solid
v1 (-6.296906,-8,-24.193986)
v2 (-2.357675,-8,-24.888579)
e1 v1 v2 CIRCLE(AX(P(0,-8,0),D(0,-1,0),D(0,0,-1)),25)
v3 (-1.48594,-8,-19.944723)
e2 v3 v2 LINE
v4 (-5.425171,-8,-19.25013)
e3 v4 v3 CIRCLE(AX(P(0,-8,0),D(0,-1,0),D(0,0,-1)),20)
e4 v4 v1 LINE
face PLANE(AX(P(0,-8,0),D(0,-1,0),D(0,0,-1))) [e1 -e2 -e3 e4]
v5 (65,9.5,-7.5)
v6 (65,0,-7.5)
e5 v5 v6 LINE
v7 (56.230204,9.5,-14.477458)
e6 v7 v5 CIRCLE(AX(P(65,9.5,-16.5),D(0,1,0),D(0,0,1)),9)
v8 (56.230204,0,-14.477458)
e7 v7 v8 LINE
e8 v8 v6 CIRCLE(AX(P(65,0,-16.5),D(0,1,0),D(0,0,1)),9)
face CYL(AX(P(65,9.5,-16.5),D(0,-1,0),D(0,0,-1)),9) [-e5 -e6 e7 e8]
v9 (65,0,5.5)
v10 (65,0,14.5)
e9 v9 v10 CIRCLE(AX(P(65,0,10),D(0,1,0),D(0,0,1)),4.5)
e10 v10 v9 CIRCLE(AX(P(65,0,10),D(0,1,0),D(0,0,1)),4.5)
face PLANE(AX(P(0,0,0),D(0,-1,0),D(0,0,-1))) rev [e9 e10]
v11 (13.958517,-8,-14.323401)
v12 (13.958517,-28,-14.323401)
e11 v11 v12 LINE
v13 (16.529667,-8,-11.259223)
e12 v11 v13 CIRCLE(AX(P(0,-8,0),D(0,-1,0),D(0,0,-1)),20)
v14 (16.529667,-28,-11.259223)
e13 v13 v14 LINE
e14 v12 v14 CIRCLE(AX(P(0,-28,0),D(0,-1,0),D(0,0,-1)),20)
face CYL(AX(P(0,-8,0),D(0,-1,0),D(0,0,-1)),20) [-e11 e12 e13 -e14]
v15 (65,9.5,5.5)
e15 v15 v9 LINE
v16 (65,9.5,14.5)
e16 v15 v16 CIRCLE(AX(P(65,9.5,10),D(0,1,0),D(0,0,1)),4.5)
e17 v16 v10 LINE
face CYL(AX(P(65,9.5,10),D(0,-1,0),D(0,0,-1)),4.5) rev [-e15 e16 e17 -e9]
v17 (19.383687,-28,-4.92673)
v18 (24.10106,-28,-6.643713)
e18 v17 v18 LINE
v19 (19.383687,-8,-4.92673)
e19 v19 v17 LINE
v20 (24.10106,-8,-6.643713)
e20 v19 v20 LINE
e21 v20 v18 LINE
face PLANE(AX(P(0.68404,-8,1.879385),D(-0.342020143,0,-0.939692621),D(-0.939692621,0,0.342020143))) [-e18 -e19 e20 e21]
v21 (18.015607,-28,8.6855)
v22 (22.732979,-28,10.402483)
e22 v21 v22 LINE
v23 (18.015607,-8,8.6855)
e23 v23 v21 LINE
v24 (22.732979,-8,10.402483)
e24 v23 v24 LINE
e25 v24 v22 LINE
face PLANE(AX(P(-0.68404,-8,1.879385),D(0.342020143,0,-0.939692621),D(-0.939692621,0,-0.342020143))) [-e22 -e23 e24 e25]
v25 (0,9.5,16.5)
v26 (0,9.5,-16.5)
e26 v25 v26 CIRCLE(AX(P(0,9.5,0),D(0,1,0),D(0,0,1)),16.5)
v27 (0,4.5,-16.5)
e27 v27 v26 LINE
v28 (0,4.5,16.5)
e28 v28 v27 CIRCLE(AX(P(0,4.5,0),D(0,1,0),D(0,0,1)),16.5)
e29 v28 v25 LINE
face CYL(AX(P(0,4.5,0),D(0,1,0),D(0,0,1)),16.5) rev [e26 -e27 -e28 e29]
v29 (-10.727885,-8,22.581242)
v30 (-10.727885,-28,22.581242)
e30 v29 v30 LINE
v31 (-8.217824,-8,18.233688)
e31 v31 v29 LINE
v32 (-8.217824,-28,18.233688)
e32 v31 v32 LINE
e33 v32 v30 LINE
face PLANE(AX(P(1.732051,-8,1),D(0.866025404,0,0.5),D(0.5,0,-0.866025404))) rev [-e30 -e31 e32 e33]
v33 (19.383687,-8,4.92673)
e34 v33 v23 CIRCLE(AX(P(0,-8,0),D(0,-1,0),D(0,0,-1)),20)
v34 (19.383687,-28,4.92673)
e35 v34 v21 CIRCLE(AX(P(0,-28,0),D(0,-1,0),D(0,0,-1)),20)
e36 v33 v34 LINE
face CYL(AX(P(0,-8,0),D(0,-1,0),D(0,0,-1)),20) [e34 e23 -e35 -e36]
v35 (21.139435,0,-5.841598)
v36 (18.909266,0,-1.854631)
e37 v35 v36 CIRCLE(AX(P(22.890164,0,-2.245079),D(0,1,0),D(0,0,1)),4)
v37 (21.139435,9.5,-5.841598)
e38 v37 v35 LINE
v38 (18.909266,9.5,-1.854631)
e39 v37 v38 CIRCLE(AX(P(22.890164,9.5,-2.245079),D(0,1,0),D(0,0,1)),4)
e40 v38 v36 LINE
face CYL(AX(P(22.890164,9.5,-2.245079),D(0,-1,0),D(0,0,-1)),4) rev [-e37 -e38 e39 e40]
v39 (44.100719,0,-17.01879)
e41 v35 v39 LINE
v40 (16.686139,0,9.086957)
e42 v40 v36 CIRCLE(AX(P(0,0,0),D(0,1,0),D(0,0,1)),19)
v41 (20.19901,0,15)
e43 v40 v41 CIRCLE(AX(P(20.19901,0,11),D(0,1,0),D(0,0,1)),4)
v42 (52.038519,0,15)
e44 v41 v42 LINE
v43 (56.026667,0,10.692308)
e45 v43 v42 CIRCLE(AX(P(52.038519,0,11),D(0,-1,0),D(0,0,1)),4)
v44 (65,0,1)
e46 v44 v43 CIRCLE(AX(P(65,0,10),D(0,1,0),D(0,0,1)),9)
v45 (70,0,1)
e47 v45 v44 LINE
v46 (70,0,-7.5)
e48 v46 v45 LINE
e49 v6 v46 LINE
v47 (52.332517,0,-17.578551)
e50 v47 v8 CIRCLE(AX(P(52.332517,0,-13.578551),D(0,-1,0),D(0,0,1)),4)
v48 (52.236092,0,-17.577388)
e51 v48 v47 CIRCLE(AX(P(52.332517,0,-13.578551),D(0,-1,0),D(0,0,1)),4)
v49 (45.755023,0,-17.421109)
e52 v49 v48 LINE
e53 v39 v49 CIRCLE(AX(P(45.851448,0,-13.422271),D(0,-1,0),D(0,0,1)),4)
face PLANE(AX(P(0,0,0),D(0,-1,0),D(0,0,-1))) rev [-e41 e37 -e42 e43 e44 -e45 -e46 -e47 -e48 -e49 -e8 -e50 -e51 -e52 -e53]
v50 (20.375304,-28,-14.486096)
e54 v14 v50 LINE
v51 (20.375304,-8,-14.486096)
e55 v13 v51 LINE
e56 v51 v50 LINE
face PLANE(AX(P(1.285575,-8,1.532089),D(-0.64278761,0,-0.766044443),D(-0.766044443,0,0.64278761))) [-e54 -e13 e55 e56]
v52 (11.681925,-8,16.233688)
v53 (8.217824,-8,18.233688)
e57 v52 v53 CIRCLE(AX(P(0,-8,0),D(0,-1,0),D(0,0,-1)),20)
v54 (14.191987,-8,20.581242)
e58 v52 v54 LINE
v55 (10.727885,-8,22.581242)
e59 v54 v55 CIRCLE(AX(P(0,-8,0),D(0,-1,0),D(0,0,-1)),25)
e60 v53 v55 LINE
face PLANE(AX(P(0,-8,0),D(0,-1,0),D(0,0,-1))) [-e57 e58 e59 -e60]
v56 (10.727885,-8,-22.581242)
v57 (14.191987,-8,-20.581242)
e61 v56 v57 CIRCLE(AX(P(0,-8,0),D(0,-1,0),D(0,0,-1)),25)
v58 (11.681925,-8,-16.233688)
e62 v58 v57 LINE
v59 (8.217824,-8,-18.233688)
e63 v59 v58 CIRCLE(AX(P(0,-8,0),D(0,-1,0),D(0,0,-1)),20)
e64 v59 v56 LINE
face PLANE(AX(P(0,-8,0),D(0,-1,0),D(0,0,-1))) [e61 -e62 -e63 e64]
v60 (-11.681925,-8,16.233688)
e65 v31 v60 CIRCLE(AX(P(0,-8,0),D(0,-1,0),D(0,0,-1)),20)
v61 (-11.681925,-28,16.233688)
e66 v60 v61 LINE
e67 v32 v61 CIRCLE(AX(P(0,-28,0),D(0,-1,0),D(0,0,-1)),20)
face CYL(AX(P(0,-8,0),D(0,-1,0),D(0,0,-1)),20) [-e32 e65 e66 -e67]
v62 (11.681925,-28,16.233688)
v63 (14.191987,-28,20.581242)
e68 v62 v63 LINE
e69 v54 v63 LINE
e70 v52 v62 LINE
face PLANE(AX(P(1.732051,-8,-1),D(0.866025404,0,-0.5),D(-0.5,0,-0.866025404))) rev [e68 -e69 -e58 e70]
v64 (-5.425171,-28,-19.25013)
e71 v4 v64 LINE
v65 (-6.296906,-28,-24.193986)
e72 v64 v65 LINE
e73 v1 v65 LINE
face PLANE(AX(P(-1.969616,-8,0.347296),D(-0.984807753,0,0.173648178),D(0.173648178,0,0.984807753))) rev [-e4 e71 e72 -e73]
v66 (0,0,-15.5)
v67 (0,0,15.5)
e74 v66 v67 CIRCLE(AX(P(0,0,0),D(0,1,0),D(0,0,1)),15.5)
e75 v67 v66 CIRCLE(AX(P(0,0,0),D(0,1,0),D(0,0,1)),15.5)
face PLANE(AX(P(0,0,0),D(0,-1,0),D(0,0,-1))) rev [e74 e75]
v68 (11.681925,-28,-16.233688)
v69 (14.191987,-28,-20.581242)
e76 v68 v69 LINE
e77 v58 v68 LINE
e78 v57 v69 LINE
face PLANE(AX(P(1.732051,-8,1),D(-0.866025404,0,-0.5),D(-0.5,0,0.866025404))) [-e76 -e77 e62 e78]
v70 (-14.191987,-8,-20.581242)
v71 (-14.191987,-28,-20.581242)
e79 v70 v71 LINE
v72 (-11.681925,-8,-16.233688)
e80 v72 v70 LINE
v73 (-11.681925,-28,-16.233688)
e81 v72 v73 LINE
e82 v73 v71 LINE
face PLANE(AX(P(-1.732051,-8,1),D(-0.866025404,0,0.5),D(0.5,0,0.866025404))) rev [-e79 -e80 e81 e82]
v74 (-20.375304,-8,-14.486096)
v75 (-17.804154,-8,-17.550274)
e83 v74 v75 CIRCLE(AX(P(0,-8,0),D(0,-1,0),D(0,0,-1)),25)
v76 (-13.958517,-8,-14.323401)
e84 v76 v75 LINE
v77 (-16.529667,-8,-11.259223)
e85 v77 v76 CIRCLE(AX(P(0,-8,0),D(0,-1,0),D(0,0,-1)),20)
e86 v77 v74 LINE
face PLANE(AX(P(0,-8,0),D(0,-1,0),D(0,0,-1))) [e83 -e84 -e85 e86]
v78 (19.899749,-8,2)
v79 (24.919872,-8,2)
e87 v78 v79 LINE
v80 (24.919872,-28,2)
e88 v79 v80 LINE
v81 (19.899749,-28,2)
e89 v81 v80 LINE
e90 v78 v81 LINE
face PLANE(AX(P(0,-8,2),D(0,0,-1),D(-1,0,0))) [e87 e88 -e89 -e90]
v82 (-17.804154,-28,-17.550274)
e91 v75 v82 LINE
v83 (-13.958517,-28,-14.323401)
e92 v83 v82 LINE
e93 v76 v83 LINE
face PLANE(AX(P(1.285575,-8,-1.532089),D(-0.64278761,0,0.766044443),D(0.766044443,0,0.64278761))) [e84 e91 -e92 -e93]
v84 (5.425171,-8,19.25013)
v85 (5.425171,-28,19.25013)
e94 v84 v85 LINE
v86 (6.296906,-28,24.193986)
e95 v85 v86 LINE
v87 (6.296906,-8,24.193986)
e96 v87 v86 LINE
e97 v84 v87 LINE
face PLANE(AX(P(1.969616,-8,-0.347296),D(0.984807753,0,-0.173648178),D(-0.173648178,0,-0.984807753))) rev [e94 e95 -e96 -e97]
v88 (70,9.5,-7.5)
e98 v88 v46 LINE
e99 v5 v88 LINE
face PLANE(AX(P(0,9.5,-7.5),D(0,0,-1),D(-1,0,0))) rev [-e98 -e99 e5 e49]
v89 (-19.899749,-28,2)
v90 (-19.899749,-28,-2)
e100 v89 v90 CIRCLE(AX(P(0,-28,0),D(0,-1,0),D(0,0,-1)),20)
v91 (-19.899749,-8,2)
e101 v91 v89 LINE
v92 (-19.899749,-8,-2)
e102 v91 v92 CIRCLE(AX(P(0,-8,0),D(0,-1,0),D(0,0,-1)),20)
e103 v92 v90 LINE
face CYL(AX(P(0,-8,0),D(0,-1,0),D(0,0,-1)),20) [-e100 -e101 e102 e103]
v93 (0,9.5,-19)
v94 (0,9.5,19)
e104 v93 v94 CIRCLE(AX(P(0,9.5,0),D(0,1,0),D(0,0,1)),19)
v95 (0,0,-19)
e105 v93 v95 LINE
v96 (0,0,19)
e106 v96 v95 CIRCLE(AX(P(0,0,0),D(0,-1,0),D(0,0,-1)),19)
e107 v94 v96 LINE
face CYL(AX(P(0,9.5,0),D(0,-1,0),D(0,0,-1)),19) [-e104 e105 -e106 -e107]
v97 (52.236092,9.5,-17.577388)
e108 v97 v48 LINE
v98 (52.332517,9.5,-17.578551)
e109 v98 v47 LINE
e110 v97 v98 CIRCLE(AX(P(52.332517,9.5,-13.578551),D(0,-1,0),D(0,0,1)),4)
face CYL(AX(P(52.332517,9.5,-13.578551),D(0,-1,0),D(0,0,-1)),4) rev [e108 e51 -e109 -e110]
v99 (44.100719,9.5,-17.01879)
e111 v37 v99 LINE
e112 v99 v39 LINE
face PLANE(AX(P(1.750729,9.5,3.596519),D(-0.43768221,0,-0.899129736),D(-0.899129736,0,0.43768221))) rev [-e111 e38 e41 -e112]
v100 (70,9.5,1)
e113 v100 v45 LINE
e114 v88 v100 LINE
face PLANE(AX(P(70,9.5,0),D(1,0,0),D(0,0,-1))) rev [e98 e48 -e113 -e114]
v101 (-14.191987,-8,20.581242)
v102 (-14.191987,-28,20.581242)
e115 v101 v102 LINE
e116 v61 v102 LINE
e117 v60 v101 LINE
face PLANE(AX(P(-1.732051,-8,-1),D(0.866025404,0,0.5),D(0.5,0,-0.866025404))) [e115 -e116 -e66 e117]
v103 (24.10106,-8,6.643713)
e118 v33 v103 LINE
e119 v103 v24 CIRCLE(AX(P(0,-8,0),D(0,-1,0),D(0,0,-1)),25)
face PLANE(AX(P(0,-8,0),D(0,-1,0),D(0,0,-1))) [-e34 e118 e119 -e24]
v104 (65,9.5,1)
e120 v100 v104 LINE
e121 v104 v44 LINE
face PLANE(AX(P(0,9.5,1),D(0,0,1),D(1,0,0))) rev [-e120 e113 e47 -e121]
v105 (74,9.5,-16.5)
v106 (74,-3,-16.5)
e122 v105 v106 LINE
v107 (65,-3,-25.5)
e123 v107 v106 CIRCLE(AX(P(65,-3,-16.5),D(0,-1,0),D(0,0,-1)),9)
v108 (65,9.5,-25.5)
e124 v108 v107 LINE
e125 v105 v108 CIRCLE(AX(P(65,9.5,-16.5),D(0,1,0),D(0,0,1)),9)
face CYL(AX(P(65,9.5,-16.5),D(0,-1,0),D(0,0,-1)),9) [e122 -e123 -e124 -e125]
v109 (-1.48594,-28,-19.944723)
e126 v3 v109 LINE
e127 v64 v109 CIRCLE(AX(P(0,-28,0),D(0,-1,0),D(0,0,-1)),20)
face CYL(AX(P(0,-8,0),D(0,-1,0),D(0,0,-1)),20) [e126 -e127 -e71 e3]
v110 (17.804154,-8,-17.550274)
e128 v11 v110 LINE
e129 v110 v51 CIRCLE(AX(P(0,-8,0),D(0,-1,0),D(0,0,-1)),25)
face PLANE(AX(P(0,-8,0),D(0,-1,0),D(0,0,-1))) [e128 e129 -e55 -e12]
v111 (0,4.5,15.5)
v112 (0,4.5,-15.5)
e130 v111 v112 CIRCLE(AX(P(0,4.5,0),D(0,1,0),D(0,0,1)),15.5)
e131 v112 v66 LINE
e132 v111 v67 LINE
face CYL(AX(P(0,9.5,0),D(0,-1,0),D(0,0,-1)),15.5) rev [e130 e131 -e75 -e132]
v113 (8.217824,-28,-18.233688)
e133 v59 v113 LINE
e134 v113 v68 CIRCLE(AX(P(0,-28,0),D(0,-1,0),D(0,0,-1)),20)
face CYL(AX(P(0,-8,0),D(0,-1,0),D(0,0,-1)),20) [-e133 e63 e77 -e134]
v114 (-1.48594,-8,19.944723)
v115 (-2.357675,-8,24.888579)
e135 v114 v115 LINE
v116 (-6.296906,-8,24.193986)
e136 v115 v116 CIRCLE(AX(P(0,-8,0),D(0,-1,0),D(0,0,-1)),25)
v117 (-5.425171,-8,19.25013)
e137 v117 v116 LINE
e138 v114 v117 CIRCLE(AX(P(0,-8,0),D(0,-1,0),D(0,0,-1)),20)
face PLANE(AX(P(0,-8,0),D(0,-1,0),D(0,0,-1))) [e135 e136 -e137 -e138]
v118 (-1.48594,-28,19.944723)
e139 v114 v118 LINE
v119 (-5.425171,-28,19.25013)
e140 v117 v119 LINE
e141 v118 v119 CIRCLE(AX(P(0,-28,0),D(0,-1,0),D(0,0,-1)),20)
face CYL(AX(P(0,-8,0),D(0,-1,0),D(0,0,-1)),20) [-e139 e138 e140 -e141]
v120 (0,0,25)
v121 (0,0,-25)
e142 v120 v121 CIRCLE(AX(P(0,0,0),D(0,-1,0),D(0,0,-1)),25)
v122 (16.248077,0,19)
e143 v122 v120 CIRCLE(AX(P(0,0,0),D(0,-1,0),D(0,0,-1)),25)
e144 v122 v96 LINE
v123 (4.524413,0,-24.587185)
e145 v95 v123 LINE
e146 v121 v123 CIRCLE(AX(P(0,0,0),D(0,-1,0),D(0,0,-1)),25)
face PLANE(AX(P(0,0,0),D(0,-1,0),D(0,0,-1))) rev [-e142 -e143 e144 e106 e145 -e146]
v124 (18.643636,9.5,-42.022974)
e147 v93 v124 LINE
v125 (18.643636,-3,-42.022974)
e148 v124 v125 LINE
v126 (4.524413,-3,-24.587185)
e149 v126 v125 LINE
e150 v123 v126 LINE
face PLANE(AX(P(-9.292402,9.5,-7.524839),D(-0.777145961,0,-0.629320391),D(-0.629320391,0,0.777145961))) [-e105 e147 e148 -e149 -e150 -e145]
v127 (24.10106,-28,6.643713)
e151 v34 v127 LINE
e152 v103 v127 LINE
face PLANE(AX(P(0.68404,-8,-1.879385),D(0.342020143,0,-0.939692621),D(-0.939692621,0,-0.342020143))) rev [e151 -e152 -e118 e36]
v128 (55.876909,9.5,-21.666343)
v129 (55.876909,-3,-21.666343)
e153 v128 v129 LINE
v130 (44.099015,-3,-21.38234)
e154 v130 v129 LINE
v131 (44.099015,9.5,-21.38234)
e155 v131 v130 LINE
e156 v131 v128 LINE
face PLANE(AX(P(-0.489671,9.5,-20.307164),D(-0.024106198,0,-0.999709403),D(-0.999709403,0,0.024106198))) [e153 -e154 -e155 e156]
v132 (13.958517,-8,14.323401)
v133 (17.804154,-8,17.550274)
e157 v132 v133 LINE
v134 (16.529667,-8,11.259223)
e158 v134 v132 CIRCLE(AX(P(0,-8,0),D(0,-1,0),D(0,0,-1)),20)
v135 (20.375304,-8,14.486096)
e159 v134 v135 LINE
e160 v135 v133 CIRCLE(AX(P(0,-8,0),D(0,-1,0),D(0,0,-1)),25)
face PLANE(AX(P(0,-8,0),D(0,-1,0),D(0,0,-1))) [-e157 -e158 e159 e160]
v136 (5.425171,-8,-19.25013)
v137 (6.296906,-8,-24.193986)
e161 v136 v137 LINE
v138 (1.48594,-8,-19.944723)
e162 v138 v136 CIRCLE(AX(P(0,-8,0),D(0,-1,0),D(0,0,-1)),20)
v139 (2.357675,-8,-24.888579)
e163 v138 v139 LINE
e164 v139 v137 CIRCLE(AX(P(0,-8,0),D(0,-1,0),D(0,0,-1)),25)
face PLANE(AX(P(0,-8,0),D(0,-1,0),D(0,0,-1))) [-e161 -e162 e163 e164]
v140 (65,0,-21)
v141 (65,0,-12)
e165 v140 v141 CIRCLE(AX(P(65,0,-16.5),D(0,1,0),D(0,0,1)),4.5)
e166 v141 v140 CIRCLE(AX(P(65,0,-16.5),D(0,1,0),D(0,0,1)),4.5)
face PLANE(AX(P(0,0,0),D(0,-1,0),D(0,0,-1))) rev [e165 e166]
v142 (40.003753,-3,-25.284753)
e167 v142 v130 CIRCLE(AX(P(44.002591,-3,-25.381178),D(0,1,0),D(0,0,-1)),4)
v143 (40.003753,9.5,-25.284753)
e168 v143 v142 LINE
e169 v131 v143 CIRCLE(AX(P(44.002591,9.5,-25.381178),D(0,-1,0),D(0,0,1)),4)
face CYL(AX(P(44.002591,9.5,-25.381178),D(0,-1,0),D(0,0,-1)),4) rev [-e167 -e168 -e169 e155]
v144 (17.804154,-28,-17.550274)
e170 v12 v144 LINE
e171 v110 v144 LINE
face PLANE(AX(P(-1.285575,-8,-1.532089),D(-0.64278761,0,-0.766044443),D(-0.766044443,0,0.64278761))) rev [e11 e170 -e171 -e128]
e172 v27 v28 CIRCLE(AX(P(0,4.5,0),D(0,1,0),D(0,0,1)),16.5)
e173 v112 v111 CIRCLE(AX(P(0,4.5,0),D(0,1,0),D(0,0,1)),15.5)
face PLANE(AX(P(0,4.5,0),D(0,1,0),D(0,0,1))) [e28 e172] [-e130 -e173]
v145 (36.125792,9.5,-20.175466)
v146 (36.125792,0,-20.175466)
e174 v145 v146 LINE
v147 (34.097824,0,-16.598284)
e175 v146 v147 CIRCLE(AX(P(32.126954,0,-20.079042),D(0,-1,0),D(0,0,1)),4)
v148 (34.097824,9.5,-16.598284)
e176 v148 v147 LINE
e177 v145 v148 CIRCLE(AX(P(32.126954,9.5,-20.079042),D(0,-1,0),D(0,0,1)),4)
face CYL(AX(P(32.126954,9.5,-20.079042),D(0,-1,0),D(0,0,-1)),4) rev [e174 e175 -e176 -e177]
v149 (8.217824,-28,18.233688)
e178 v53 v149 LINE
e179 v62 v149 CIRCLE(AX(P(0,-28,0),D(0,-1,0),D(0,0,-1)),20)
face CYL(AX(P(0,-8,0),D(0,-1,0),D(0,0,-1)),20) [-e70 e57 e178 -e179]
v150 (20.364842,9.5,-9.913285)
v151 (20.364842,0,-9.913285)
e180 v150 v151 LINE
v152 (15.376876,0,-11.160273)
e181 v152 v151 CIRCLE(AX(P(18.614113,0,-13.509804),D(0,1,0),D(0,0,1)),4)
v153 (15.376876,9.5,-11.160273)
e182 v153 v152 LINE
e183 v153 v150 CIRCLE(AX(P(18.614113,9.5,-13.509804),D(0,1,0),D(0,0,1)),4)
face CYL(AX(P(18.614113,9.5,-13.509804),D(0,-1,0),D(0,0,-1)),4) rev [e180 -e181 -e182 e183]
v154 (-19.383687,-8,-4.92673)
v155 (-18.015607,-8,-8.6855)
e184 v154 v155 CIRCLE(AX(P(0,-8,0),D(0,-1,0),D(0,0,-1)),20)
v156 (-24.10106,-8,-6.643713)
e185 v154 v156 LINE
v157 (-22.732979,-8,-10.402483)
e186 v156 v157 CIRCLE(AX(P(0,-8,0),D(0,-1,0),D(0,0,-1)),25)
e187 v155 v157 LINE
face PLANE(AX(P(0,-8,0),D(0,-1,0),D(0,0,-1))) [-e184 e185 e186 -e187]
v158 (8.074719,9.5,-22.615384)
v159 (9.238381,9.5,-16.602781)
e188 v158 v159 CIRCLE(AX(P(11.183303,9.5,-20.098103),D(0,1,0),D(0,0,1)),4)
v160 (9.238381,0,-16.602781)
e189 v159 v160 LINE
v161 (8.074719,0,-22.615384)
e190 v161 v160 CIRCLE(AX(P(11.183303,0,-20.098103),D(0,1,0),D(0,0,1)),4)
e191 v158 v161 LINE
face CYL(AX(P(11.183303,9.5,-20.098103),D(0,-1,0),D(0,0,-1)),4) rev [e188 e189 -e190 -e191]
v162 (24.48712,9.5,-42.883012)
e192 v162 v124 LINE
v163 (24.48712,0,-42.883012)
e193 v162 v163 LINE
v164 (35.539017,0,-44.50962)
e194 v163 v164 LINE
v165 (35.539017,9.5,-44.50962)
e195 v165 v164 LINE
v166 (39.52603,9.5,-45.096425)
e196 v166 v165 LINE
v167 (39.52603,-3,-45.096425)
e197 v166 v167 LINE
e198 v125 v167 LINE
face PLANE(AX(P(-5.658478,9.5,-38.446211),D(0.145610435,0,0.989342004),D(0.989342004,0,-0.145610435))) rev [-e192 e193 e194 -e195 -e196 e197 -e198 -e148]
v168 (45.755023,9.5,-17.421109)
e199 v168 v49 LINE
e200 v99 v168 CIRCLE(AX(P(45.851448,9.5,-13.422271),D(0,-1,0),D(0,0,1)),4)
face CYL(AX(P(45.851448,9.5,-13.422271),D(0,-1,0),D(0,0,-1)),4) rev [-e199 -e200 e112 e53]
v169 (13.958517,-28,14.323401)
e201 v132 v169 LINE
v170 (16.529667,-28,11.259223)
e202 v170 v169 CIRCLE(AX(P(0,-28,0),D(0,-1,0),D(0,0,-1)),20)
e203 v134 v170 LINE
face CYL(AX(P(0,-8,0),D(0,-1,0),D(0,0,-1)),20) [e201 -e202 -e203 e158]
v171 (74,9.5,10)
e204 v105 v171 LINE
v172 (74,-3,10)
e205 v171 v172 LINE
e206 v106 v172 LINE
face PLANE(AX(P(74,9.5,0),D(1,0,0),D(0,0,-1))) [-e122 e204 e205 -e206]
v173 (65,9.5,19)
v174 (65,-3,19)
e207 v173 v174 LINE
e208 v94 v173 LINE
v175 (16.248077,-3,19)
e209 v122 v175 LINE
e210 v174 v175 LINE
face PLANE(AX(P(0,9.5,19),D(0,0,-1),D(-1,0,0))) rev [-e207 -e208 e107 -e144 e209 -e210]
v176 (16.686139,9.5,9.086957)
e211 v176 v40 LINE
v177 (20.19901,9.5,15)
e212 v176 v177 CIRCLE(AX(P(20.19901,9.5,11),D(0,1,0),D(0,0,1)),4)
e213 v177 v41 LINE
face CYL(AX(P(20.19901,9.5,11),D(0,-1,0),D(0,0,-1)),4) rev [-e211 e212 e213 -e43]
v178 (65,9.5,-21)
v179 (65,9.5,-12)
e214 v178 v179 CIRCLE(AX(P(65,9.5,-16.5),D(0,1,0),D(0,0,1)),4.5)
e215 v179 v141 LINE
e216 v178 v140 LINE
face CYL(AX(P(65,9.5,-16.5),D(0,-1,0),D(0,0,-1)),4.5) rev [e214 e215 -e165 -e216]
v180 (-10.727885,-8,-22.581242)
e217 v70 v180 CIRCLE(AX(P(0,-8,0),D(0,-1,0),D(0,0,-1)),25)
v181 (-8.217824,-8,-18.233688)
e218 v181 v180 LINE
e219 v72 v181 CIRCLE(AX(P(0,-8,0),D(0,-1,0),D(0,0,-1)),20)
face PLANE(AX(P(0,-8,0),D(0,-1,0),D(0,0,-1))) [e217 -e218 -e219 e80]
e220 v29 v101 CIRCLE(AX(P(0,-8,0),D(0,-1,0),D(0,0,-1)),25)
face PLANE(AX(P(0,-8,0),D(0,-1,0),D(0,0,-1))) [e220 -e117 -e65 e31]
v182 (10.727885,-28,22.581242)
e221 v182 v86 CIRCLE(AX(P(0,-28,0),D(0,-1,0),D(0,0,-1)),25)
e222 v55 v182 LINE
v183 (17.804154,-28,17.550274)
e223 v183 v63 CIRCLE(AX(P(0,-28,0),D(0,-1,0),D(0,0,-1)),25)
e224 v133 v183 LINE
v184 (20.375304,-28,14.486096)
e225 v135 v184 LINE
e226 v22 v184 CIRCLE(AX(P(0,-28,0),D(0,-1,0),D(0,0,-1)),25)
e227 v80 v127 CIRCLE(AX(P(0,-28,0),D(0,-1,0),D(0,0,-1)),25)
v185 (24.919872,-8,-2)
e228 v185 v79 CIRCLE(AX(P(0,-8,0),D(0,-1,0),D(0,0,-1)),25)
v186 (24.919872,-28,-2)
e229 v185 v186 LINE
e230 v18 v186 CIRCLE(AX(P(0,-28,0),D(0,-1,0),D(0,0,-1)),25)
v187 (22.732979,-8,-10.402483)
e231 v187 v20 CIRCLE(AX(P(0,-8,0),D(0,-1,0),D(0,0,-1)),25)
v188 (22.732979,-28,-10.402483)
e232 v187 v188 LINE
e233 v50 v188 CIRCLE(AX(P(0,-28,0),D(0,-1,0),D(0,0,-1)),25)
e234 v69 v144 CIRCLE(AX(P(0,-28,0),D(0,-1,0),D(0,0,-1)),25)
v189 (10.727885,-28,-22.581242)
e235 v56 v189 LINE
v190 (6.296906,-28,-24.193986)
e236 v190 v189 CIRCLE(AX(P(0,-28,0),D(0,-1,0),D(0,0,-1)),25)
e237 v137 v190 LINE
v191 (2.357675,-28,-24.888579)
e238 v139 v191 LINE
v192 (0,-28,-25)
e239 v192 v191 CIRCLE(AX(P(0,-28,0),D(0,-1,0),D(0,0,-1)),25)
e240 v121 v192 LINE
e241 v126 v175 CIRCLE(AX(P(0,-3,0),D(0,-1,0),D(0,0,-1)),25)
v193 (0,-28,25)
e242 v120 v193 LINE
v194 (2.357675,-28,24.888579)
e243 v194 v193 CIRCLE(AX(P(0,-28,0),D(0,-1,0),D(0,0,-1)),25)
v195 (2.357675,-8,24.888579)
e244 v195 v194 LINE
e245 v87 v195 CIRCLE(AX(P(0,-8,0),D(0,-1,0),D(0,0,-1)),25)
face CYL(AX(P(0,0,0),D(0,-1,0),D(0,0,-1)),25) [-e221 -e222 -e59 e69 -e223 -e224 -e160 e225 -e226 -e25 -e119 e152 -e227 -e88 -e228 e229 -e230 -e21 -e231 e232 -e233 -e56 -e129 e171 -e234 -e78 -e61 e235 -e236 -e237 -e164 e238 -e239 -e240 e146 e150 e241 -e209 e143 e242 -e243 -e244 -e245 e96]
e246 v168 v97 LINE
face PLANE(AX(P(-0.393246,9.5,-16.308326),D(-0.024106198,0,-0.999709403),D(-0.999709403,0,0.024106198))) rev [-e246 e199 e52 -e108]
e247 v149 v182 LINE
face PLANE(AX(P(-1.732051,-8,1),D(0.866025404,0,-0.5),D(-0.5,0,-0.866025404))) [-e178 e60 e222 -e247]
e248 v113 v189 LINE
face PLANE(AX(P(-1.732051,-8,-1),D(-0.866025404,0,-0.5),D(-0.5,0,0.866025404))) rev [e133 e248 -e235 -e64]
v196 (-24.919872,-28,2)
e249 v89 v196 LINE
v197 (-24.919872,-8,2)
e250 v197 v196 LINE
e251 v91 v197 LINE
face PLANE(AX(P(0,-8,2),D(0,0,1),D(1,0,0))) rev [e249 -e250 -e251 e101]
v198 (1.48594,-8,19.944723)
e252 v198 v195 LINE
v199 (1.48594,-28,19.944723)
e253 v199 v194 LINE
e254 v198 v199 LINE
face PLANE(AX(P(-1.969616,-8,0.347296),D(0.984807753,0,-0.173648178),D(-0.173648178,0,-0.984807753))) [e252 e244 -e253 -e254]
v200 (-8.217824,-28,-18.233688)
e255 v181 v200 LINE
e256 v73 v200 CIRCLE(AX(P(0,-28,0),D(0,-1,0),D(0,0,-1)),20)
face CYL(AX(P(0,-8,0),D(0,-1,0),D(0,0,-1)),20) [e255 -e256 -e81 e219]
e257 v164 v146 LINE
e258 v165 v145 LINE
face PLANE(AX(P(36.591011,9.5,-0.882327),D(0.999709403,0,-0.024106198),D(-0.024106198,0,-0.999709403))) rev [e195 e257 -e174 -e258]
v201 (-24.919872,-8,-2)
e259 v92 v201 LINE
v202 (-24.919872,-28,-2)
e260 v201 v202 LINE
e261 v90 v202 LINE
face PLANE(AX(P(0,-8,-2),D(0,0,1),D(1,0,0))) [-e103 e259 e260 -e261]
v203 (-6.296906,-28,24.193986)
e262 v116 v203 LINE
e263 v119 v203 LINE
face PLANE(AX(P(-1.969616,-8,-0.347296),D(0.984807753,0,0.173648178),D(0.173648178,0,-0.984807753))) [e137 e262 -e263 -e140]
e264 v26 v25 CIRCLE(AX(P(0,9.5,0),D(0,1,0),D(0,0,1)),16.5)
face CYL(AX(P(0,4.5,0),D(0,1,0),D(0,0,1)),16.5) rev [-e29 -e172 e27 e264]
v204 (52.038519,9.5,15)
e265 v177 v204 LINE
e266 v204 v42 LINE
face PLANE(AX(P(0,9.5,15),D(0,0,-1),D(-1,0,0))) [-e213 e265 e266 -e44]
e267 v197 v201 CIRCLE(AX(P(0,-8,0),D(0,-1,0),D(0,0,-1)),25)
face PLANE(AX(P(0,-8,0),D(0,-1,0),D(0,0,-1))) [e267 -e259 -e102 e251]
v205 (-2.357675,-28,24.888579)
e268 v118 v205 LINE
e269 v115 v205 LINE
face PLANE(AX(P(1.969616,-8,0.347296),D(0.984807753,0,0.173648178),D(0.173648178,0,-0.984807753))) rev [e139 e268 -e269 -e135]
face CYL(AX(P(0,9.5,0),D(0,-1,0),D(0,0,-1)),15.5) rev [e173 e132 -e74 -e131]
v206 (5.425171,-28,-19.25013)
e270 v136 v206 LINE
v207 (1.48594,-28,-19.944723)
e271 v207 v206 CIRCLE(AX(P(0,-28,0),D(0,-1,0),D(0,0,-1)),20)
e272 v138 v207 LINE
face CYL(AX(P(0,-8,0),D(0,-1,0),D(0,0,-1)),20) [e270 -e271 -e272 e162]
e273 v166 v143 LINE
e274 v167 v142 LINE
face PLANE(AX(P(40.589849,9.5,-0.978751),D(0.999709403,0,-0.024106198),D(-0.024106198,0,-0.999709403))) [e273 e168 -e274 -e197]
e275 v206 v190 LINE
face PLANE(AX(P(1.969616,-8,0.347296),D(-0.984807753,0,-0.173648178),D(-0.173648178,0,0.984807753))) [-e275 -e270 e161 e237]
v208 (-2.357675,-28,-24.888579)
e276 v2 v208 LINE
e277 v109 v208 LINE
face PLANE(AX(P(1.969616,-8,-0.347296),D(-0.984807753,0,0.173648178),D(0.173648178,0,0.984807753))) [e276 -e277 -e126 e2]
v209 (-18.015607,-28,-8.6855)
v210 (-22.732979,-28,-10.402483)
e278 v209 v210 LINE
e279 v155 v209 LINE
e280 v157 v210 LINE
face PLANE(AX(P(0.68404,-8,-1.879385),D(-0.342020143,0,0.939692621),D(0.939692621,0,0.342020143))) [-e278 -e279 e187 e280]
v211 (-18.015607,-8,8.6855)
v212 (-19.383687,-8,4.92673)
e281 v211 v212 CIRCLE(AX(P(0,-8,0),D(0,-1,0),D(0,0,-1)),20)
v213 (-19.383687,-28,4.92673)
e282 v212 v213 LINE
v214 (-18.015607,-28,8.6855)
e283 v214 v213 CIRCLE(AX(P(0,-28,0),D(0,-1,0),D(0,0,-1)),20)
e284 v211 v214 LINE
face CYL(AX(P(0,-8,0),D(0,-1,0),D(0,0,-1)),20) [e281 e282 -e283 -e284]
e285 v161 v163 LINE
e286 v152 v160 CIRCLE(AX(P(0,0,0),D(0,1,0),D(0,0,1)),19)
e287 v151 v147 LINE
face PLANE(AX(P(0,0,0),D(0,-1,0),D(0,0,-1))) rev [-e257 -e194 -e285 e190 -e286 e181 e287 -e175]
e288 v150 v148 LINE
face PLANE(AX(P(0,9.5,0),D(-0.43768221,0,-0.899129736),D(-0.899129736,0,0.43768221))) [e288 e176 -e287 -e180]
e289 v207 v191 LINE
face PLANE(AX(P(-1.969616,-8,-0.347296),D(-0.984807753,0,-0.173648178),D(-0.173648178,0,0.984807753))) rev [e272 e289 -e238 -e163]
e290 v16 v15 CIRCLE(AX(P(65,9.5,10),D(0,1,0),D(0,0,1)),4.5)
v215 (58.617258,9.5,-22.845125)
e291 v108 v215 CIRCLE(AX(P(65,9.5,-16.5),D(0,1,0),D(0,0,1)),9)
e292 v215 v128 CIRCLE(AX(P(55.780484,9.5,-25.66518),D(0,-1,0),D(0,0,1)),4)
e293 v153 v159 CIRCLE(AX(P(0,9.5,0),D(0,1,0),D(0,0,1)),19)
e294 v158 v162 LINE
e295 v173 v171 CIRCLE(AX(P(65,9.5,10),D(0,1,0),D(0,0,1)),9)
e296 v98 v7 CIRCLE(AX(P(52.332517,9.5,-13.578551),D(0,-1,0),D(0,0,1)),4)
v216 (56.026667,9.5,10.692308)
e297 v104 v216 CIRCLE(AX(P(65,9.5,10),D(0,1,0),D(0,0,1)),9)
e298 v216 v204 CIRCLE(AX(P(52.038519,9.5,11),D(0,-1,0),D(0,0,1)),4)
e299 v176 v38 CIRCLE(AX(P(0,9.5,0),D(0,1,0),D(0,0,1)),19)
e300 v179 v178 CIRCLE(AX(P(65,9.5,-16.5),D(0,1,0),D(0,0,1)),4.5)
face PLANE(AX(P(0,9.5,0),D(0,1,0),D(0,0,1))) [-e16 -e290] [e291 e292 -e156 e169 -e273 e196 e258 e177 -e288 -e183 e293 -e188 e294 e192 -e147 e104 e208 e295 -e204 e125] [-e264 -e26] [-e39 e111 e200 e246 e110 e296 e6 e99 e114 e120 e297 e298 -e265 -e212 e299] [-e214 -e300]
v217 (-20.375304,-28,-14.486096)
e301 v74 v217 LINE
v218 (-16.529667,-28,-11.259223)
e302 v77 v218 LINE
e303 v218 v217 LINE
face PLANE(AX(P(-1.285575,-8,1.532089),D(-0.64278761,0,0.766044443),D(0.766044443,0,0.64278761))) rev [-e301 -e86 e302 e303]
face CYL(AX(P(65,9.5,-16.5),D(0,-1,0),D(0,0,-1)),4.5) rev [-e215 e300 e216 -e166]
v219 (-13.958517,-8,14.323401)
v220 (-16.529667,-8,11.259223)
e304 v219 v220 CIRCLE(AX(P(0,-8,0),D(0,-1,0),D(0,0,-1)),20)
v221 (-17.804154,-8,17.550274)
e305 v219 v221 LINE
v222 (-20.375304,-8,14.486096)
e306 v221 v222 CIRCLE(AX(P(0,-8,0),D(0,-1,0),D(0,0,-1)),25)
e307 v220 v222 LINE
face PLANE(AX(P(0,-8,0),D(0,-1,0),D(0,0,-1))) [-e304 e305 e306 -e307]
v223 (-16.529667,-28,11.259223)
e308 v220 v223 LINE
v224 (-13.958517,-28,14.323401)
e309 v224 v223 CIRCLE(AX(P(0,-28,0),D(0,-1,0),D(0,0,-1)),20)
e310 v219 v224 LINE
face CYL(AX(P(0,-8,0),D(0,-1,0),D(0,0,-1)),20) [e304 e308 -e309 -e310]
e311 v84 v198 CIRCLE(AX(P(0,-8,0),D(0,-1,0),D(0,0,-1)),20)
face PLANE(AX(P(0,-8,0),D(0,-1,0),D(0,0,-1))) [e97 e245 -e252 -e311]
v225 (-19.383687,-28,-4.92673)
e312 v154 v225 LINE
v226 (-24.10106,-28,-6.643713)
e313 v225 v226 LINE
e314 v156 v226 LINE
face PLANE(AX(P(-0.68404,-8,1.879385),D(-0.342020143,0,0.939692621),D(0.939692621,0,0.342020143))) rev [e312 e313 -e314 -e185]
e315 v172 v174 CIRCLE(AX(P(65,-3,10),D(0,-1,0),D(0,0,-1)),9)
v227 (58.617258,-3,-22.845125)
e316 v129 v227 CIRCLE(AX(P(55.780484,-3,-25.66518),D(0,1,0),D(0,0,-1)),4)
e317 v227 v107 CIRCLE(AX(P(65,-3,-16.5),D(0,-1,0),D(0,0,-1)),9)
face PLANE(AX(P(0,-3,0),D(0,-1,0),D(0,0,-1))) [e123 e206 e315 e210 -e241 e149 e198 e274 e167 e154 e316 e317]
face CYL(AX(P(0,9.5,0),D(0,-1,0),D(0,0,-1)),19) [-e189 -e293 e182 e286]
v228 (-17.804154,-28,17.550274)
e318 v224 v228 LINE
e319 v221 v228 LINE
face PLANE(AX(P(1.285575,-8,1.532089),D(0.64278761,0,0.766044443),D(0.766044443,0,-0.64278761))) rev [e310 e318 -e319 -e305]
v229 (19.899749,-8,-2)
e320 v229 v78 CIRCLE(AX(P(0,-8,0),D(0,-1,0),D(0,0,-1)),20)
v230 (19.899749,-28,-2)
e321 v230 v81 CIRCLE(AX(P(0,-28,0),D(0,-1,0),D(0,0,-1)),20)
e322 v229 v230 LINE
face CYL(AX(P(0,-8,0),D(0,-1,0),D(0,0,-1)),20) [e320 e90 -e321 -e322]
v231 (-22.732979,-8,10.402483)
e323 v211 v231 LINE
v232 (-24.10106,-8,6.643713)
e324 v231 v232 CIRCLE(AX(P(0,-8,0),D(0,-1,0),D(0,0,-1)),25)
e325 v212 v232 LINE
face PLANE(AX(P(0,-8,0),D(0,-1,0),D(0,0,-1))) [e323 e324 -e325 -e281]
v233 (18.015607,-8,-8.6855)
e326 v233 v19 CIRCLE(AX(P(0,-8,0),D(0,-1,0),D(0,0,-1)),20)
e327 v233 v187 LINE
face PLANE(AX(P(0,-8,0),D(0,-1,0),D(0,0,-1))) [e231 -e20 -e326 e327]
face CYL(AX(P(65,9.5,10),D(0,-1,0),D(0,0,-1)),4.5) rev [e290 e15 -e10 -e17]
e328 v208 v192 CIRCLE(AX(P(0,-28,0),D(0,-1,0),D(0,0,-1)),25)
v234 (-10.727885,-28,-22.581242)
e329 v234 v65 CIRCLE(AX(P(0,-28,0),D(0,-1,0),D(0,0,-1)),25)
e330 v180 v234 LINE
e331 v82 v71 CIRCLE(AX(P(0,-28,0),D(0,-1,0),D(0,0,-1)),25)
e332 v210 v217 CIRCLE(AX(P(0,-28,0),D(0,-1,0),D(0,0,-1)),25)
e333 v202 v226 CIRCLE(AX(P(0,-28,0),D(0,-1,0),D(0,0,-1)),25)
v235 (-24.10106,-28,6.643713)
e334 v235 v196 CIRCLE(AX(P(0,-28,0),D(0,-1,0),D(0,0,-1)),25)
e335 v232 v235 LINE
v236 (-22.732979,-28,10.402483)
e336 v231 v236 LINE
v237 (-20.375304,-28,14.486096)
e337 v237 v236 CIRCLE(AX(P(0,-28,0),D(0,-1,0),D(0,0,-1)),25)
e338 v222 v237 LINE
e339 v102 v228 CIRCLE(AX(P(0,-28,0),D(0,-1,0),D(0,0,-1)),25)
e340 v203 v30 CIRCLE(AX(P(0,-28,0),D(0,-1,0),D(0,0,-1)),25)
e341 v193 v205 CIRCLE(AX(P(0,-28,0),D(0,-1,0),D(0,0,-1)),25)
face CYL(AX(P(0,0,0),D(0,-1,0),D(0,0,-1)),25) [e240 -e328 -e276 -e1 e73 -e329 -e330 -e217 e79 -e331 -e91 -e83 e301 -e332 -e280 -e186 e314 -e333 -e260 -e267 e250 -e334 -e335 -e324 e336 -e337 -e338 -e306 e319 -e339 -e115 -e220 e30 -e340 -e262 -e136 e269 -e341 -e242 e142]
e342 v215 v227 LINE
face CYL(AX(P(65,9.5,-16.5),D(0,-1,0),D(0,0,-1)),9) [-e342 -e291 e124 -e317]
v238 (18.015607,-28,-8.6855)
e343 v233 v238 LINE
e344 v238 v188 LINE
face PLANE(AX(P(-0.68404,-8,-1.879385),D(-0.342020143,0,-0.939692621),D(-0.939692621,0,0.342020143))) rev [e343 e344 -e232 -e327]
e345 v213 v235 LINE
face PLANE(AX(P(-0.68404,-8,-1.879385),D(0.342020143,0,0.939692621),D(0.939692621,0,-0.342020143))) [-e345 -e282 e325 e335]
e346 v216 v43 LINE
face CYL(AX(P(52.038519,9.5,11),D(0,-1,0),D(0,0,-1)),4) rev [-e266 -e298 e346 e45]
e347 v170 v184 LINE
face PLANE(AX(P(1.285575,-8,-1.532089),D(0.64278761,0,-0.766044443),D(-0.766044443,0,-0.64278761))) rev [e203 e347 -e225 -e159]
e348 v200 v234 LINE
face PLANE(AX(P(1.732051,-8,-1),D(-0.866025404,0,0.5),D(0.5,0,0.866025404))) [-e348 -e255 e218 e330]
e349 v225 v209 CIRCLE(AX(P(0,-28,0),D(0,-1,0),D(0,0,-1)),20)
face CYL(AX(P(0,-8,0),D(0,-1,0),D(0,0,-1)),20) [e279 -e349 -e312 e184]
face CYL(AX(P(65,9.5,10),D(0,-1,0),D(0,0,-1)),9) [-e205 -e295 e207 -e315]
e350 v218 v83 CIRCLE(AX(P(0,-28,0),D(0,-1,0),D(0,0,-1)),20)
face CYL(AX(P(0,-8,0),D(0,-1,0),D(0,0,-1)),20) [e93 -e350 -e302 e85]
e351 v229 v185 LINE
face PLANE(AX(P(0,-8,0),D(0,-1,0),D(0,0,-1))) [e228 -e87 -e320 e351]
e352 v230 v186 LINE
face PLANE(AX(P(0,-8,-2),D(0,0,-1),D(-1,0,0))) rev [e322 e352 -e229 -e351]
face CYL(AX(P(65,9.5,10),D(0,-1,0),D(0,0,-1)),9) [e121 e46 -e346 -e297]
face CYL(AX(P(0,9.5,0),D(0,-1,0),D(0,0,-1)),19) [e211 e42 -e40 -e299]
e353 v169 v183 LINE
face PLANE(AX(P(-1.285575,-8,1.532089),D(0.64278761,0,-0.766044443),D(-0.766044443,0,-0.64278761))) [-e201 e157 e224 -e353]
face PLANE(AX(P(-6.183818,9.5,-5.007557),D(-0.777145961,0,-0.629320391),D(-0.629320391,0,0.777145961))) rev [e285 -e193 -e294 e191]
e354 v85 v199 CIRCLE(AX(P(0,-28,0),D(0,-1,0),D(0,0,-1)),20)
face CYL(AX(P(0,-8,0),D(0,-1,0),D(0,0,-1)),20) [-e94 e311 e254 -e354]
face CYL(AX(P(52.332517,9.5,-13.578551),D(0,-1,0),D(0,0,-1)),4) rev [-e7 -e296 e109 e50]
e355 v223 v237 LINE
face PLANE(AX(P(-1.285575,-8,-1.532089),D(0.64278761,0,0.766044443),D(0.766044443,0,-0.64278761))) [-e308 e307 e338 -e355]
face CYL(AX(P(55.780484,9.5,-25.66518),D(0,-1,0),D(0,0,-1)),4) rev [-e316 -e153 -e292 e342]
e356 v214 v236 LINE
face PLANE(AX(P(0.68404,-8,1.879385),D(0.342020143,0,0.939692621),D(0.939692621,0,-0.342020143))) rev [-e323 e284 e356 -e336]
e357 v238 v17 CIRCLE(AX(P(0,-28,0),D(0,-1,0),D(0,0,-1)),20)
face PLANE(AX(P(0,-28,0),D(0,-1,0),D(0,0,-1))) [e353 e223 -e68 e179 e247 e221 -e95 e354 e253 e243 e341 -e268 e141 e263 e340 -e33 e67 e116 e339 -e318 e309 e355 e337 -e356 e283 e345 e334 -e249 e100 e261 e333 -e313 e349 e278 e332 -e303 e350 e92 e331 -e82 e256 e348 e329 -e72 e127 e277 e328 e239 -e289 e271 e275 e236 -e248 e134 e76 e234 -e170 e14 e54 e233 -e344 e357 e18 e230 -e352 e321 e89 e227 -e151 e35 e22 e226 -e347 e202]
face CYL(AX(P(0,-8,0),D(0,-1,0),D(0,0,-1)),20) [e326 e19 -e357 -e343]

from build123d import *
from build123d.topology import SkipClean

# Parameters (mm, degrees)
BRACKET_PLATE_PROFILE_R   = 15.5
BRACKET_PLATE_PROFILE_R_2 = 4.5
BRACKET_PLATE_9_5MM_DEPTH = 9.5
RAISED_START              = 3
RAISED_RIM_PROFILE_R      = 15.5
RAISED_RIM_PROFILE_R_2    = 4.5
RAISED_RIM_3MM_DEPTH      = 3
BORE_START                = -5
BORE_POCKET_PROFILE_R     = 16.5
BORE_POCKET_PROFILE_R_2   = 15.5
BORE_POCKET_33X5_DEPTH    = 5
HUB_RING_3MM_DEPTH        = 3
SPLINE_START              = 25
HUB_PROFILE_50_R          = 25
SPLINE_HUB_50X25_DEPTH    = 25
SPLINE_FINS_CUT_18X_DEPTH = 20


with BuildPart() as part:
    # Bracket Plate Profile → Bracket Plate 9.5mm (new body)
    with BuildSketch(Plane(origin=(0, 0, 0), x_dir=(1, 0, 0), z_dir=(0, 1, 0))):
        with BuildLine():
            Line((18.643636366, 42.022973535), (0, 19))
            ThreePointArc((0, 19), (-19, 0), (0, -19))
            Line((0, -19), (65, -19))
            ThreePointArc((65, -19), (71.363961031, -16.363961031), (74, -10))
            Line((74, -10), (74, 16.5))
            ThreePointArc((74, 16.5), (68.431859925, 24.819996241), (58.617258344, 22.845124818))
            ThreePointArc((58.617258344, 22.845124818), (57.361084073, 21.990713763), (55.876909068, 21.666342679))
            Line((55.876909068, 21.666342679), (44.099015371, 21.382339908))
            ThreePointArc((44.099015371, 21.382339908), (41.243168009, 22.485389703), (40.003752964, 25.284752729))
            Line((40.003752964, 25.284752729), (39.526030045, 45.096424793))
            Line((39.526030045, 45.096424793), (35.539017067, 44.509619935))
            Line((35.539017067, 44.509619935), (36.125791513, 20.175466313))
            ThreePointArc((36.125791513, 20.175466313), (35.606668042, 18.10633032), (34.097824063, 16.598284304))
            Line((34.097824063, 16.598284304), (20.364841939, 9.913284663))
            ThreePointArc((20.364841939, 9.913284663), (17.643973229, 9.629232951), (15.376876038, 11.160272546))
            ThreePointArc((15.376876038, 11.160272546), (12.604877523, 14.216788056), (9.23838051, 16.602780657))
            ThreePointArc((9.23838051, 16.602780657), (7.256175018, 19.338058171), (8.074718877, 22.615384465))
            Line((8.074718877, 22.615384465), (24.487120066, 42.883012025))
            Line((24.487120066, 42.883012025), (18.643636366, 42.022973535))
        make_face()
        with Locations(Location((0, 0, 0), (0, 0, 270))):
            Circle(BRACKET_PLATE_PROFILE_R, mode=Mode.SUBTRACT)
        with Locations(Location((65, -10, 0), (0, 0, 270))):
            Circle(BRACKET_PLATE_PROFILE_R_2, mode=Mode.SUBTRACT)
        with BuildLine():
            Line((65, 7.5), (70, 7.5))
            Line((70, 7.5), (70, -1))
            Line((70, -1), (65, -1))
            ThreePointArc((65, -1), (58.395805529, -3.885704016), (56.026666725, -10.692307692))
            ThreePointArc((56.026666725, -10.692307692), (54.973716146, -13.717464882), (52.038518603, -15))
            Line((52.038518603, -15), (20.199009877, -15))
            ThreePointArc((20.199009877, -15), (16.760102062, -13.043015674), (16.686138594, -9.086956522))
            ThreePointArc((16.686138594, -9.086956522), (18.61955403, -3.783147859), (18.909266102, 1.854630825))
            ThreePointArc((18.909266102, 1.854630825), (19.399195242, 4.197804576), (21.139435388, 5.841598366))
            Line((21.139435388, 5.841598366), (44.100719397, 17.018790179))
            ThreePointArc((44.100719397, 17.018790179), (44.906218523, 17.308984599), (45.755023444, 17.421108847))
            Line((45.755023444, 17.421108847), (52.236091905, 17.577388182))
            ThreePointArc((52.236091905, 17.577388182), (54.785023693, 16.73848877), (56.230203867, 14.477458086))
            ThreePointArc((56.230203867, 14.477458086), (59.396558077, 9.457171121), (65, 7.5))
        make_face(mode=Mode.SUBTRACT)
        with Locations(Location((65, 16.5, 0), (0, 0, 270))):
            Circle(BRACKET_PLATE_PROFILE_R_2, mode=Mode.SUBTRACT)
    extrude(amount=BRACKET_PLATE_9_5MM_DEPTH)

    # Raised Rim Profile → Raised Rim 3mm (add)
    # profile 1 of 8: a face of its own
    with SkipClean():  # the faces are left unmerged after this step: merging them gives an invalid solid
        with BuildSketch(Plane.XZ.offset(RAISED_START)):
            with BuildLine():
                ThreePointArc((16.686138594, 9.086956522), (9.704324451, 16.334812119), (0, 19))
                ThreePointArc((0, 19), (-19, 0), (0, -19))
                ThreePointArc((0, -19), (4.772167616, -18.39093299), (9.23838051, -16.602780657))
                ThreePointArc((9.23838051, -16.602780657), (12.604877523, -14.216788056), (15.376876038, -11.160272546))
                ThreePointArc((15.376876038, -11.160272546), (17.763266244, -6.742875672), (18.909266102, -1.854630825))
                ThreePointArc((18.909266102, -1.854630825), (18.977302969, -0.92842449), (19, 0))
                ThreePointArc((19, 0), (18.412450045, 4.688462793), (16.686138594, 9.086956522))
            make_face()
            with Locations(Location((0, 0, 0), (0, 0, 90))):
                Circle(RAISED_RIM_PROFILE_R, mode=Mode.SUBTRACT)
        # profile 2 of 8: a face of its own
        with BuildSketch(Plane.XZ.offset(RAISED_START)):
            with Locations(Location((0, 0, 0), (0, 0, 90))):
                Circle(RAISED_RIM_PROFILE_R)
        # profile 3 of 8: a face of its own
        with BuildSketch(Plane.XZ.offset(RAISED_START)):
            with BuildLine():
                Line((65, 19), (0, 19))
                ThreePointArc((0, 19), (9.704324451, 16.334812119), (16.686138594, 9.086956522))
                ThreePointArc((16.686138594, 9.086956522), (16.760102062, 13.043015674), (20.199009877, 15))
                Line((20.199009877, 15), (52.038518603, 15))
                ThreePointArc((52.038518603, 15), (54.973716146, 13.717464882), (56.026666725, 10.692307692))
                ThreePointArc((56.026666725, 10.692307692), (58.395805529, 3.885704016), (65, 1))
                Line((65, 1), (70, 1))
                Line((70, 1), (70, -7.5))
                Line((70, -7.5), (65, -7.5))
                ThreePointArc((65, -7.5), (59.396558077, -9.457171121), (56.230203867, -14.477458086))
                ThreePointArc((56.230203867, -14.477458086), (54.785023693, -16.73848877), (52.236091905, -17.577388182))
                Line((52.236091905, -17.577388182), (45.755023444, -17.421108847))
                ThreePointArc((45.755023444, -17.421108847), (44.906218523, -17.308984599), (44.100719397, -17.018790179))
                Line((44.100719397, -17.018790179), (21.139435388, -5.841598366))
                ThreePointArc((21.139435388, -5.841598366), (19.399195242, -4.197804576), (18.909266102, -1.854630825))
                ThreePointArc((18.909266102, -1.854630825), (17.763266244, -6.742875672), (15.376876038, -11.160272546))
                ThreePointArc((15.376876038, -11.160272546), (17.643973229, -9.629232951), (20.364841939, -9.913284663))
                Line((20.364841939, -9.913284663), (34.097824063, -16.598284304))
                ThreePointArc((34.097824063, -16.598284304), (35.606668042, -18.10633032), (36.125791513, -20.175466313))
                Line((36.125791513, -20.175466313), (35.539017067, -44.509619935))
                Line((35.539017067, -44.509619935), (39.526030045, -45.096424793))
                Line((39.526030045, -45.096424793), (40.003752964, -25.284752729))
                ThreePointArc((40.003752964, -25.284752729), (41.243168009, -22.485389703), (44.099015371, -21.382339908))
                Line((44.099015371, -21.382339908), (55.876909068, -21.666342679))
                ThreePointArc((55.876909068, -21.666342679), (57.361084073, -21.990713763), (58.617258344, -22.845124818))
                ThreePointArc((58.617258344, -22.845124818), (68.431859925, -24.819996241), (74, -16.5))
                Line((74, -16.5), (74, 10))
                ThreePointArc((74, 10), (71.363961031, 16.363961031), (65, 19))
            make_face()
            with Locations(Location((65, -16.5, 0), (0, 0, 90))):
                Circle(RAISED_RIM_PROFILE_R_2, mode=Mode.SUBTRACT)
            with Locations(Location((65, 10, 0), (0, 0, 90))):
                Circle(RAISED_RIM_PROFILE_R_2, mode=Mode.SUBTRACT)
        # profile 4 of 8: a face of its own
        with BuildSketch(Plane.XZ.offset(RAISED_START)):
            with Locations(Location((65, 10, 0), (0, 0, 90))):
                Circle(RAISED_RIM_PROFILE_R_2)
        # profile 5 of 8: a face of its own
        with BuildSketch(Plane.XZ.offset(RAISED_START)):
            with Locations(Location((65, -16.5, 0), (0, 0, 90))):
                Circle(RAISED_RIM_PROFILE_R_2)
        # profile 6 of 8: a face of its own
        with BuildSketch(Plane.XZ.offset(RAISED_START)):
            with BuildLine():
                ThreePointArc((16.686138594, 9.086956522), (16.760102062, 13.043015674), (20.199009877, 15))
                Line((20.199009877, 15), (52.038518603, 15))
                ThreePointArc((52.038518603, 15), (54.973716146, 13.717464882), (56.026666725, 10.692307692))
                ThreePointArc((56.026666725, 10.692307692), (58.395805529, 3.885704016), (65, 1))
                Line((65, 1), (70, 1))
                Line((70, 1), (70, -7.5))
                Line((70, -7.5), (65, -7.5))
                ThreePointArc((65, -7.5), (59.396558077, -9.457171121), (56.230203867, -14.477458086))
                ThreePointArc((56.230203867, -14.477458086), (54.785023693, -16.73848877), (52.236091905, -17.577388182))
                Line((52.236091905, -17.577388182), (45.755023444, -17.421108847))
                ThreePointArc((45.755023444, -17.421108847), (44.906218523, -17.308984599), (44.100719397, -17.018790179))
                Line((44.100719397, -17.018790179), (21.139435388, -5.841598366))
                ThreePointArc((21.139435388, -5.841598366), (19.399195242, -4.197804576), (18.909266102, -1.854630825))
                ThreePointArc((18.909266102, -1.854630825), (18.61955403, 3.783147859), (16.686138594, 9.086956522))
            make_face()
        # profile 7 of 8: a face of its own
        with BuildSketch(Plane.XZ.offset(RAISED_START)):
            with BuildLine():
                ThreePointArc((15.376876038, -11.160272546), (12.604877523, -14.216788056), (9.23838051, -16.602780657))
                ThreePointArc((9.23838051, -16.602780657), (7.256175018, -19.338058171), (8.074718877, -22.615384465))
                Line((8.074718877, -22.615384465), (24.487120066, -42.883012025))
                Line((24.487120066, -42.883012025), (35.539017067, -44.509619935))
                Line((35.539017067, -44.509619935), (36.125791513, -20.175466313))
                ThreePointArc((36.125791513, -20.175466313), (35.606668042, -18.10633032), (34.097824063, -16.598284304))
                Line((34.097824063, -16.598284304), (20.364841939, -9.913284663))
                ThreePointArc((20.364841939, -9.913284663), (17.643973229, -9.629232951), (15.376876038, -11.160272546))
            make_face()
        # profile 8 of 8: a face of its own
        with BuildSketch(Plane.XZ.offset(RAISED_START)):
            with BuildLine():
                ThreePointArc((9.23838051, -16.602780657), (4.772167616, -18.39093299), (0, -19))
                Line((0, -19), (18.643636366, -42.022973535))
                Line((18.643636366, -42.022973535), (24.487120066, -42.883012025))
                Line((24.487120066, -42.883012025), (8.074718877, -22.615384465))
                ThreePointArc((8.074718877, -22.615384465), (7.256175018, -19.338058171), (9.23838051, -16.602780657))
            make_face()
        extrude(amount=-RAISED_RIM_3MM_DEPTH)

    # Bore Pocket Profile → Bore Pocket Ø33x5 (cut)
    with SkipClean():  # the faces are left unmerged after this step: merging them gives an invalid solid
        with BuildSketch(Plane(origin=(0, 9.5, 0), x_dir=(1, 0, 0), z_dir=(0, 1, 0)).offset(BORE_START)):
            with Locations(Location((0, 0, 0), (0, 0, 270))):
                Circle(BORE_POCKET_PROFILE_R)
            with Locations(Location((0, 0, 0), (0, 0, 270))):
                Circle(BORE_POCKET_PROFILE_R_2, mode=Mode.SUBTRACT)
        extrude(amount=BORE_POCKET_33X5_DEPTH, mode=Mode.SUBTRACT)

    # Hub Ring Profile → Hub Ring 3mm (add)
    with BuildSketch(Plane.XZ.offset(3)):
        with BuildLine():
            Line((0, 19), (6.244997998, 19))
            ThreePointArc((6.244997998, 19), (-19.807511084, 2.768122951), (0.796921894, -19.98411658))
            Line((0.796921894, -19.98411658), (0, -19))
            ThreePointArc((0, -19), (-19, 0), (0, 19))
        make_face()
        with BuildLine():
            ThreePointArc((4.524413475, -24.587185335), (19.210808636, -15.998275893), (25, 0))
            ThreePointArc((25, 0), (22.706848309, 10.459399595), (16.248076809, 19))
            Line((16.248076809, 19), (6.244997998, 19))
            ThreePointArc((6.244997998, 19), (16.200308021, 11.728172066), (20, 0))
            ThreePointArc((20, 0), (14.421137921, -13.857517132), (0.796921894, -19.98411658))
            Line((0.796921894, -19.98411658), (4.524413475, -24.587185335))
        make_face()
        with BuildLine():
            Line((6.244997998, 19), (16.248076809, 19))
            ThreePointArc((16.248076809, 19), (-24.141971119, 6.493475994), (4.524413475, -24.587185335))
            Line((4.524413475, -24.587185335), (0.796921894, -19.98411658))
            ThreePointArc((0.796921894, -19.98411658), (-19.807511084, 2.768122951), (6.244997998, 19))
        make_face()
    extrude(amount=-HUB_RING_3MM_DEPTH)

    # Hub Profile Ø50 → Spline Hub Ø50x25 (add)
    with BuildSketch(Plane.XZ.offset(3).offset(SPLINE_START)):
        with Locations(Location((0, 0, 0), (0, 0, 270))):
            Circle(HUB_PROFILE_50_R)
    extrude(amount=-SPLINE_HUB_50X25_DEPTH)

    # Spline Fin Profile 18x → Spline Fins Cut 18x (cut)
    with BuildSketch(Plane.XZ.offset(28)):
        with BuildLine():
            ThreePointArc((-24.919871589, 2), (-25, 0), (-24.919871589, -2))
            Line((-24.919871589, -2), (-19.899748742, -2))
            ThreePointArc((-19.899748742, -2), (-20, 0), (-19.899748742, 2))
            Line((-19.899748742, 2), (-24.919871589, 2))
        make_face()
        with BuildLine():
            ThreePointArc((-24.10105973, -6.643712811), (-23.49231552, -8.550503583), (-22.732979156, -10.402483294))
            Line((-22.732979156, -10.402483294), (-18.015606762, -8.685500159))
            ThreePointArc((-18.015606762, -8.685500159), (-18.793852416, -6.840402867), (-19.383687335, -4.926729675))
            Line((-19.383687335, -4.926729675), (-24.10105973, -6.643712811))
        make_face()
        with BuildLine():
            ThreePointArc((-20.375304373, -14.486095806), (-19.151111078, -16.069690242), (-17.804153934, -17.550273578))
            Line((-17.804153934, -17.550273578), (-13.958516724, -14.323400814))
            ThreePointArc((-13.958516724, -14.323400814), (-15.320888862, -12.855752194), (-16.529667163, -11.259223041))
            Line((-16.529667163, -11.259223041), (-20.375304373, -14.486095806))
        make_face()
        with BuildLine():
            ThreePointArc((-14.191986602, -20.581241855), (-12.5, -21.650635095), (-10.727884987, -22.581241855))
            Line((-10.727884987, -22.581241855), (-8.217823563, -18.23368794))
            ThreePointArc((-8.217823563, -18.23368794), (-10, -17.320508076), (-11.681925179, -16.23368794))
            Line((-11.681925179, -16.23368794), (-14.191986602, -20.581241855))
        make_face()
        with BuildLine():
            ThreePointArc((-6.296905795, -24.193986389), (-4.341204442, -24.620193825), (-2.357674783, -24.8885791))
            Line((-2.357674783, -24.8885791), (-1.485939599, -19.9447232))
            ThreePointArc((-1.485939599, -19.9447232), (-3.472963553, -19.69615506), (-5.425170611, -19.250130489))
            Line((-5.425170611, -19.250130489), (-6.296905795, -24.193986389))
        make_face()
        with BuildLine():
            ThreePointArc((2.357674783, -24.8885791), (4.341204442, -24.620193825), (6.296905795, -24.193986389))
            Line((6.296905795, -24.193986389), (5.425170611, -19.250130489))
            ThreePointArc((5.425170611, -19.250130489), (3.472963553, -19.69615506), (1.485939599, -19.9447232))
            Line((1.485939599, -19.9447232), (2.357674783, -24.8885791))
        make_face()
        with BuildLine():
            ThreePointArc((10.727884987, -22.581241855), (12.5, -21.650635095), (14.191986602, -20.581241855))
            Line((14.191986602, -20.581241855), (11.681925179, -16.23368794))
            ThreePointArc((11.681925179, -16.23368794), (10, -17.320508076), (8.217823563, -18.23368794))
            Line((8.217823563, -18.23368794), (10.727884987, -22.581241855))
        make_face()
        with BuildLine():
            ThreePointArc((17.804153934, -17.550273578), (19.151111078, -16.069690242), (20.375304373, -14.486095806))
            Line((20.375304373, -14.486095806), (16.529667163, -11.259223041))
            ThreePointArc((16.529667163, -11.259223041), (15.320888862, -12.855752194), (13.958516724, -14.323400814))
            Line((13.958516724, -14.323400814), (17.804153934, -17.550273578))
        make_face()
        with BuildLine():
            Line((24.10105973, -6.643712811), (19.383687335, -4.926729675))
            ThreePointArc((19.383687335, -4.926729675), (18.793852416, -6.840402867), (18.015606762, -8.685500159))
            Line((18.015606762, -8.685500159), (22.732979156, -10.402483294))
            ThreePointArc((22.732979156, -10.402483294), (23.49231552, -8.550503583), (24.10105973, -6.643712811))
        make_face()
        with BuildLine():
            Line((19.899748742, -2), (24.919871589, -2))
            ThreePointArc((24.919871589, -2), (24.979959865, -1.000802248), (25, 0))
            ThreePointArc((25, 0), (24.979959865, 1.000802248), (24.919871589, 2))
            Line((24.919871589, 2), (19.899748742, 2))
            ThreePointArc((19.899748742, 2), (20, 0), (19.899748742, -2))
        make_face()
        with BuildLine():
            Line((19.383687335, 4.926729675), (24.10105973, 6.643712811))
            ThreePointArc((24.10105973, 6.643712811), (23.49231552, 8.550503583), (22.732979156, 10.402483294))
            Line((22.732979156, 10.402483294), (18.015606762, 8.685500159))
            ThreePointArc((18.015606762, 8.685500159), (18.793852416, 6.840402867), (19.383687335, 4.926729675))
        make_face()
        with BuildLine():
            Line((16.529667163, 11.259223041), (20.375304373, 14.486095806))
            ThreePointArc((20.375304373, 14.486095806), (19.151111078, 16.069690242), (17.804153934, 17.550273578))
            Line((17.804153934, 17.550273578), (13.958516724, 14.323400814))
            ThreePointArc((13.958516724, 14.323400814), (15.320888862, 12.855752194), (16.529667163, 11.259223041))
        make_face()
        with BuildLine():
            Line((11.681925179, 16.23368794), (14.191986602, 20.581241855))
            ThreePointArc((14.191986602, 20.581241855), (12.5, 21.650635095), (10.727884987, 22.581241855))
            Line((10.727884987, 22.581241855), (8.217823563, 18.23368794))
            ThreePointArc((8.217823563, 18.23368794), (10, 17.320508076), (11.681925179, 16.23368794))
        make_face()
        with BuildLine():
            Line((5.425170611, 19.250130489), (6.296905795, 24.193986389))
            ThreePointArc((6.296905795, 24.193986389), (4.341204442, 24.620193825), (2.357674783, 24.8885791))
            Line((2.357674783, 24.8885791), (1.485939599, 19.9447232))
            ThreePointArc((1.485939599, 19.9447232), (3.472963553, 19.69615506), (5.425170611, 19.250130489))
        make_face()
        with BuildLine():
            Line((-1.485939599, 19.9447232), (-2.357674783, 24.8885791))
            ThreePointArc((-2.357674783, 24.8885791), (-4.341204442, 24.620193825), (-6.296905795, 24.193986389))
            Line((-6.296905795, 24.193986389), (-5.425170611, 19.250130489))
            ThreePointArc((-5.425170611, 19.250130489), (-3.472963553, 19.69615506), (-1.485939599, 19.9447232))
        make_face()
        with BuildLine():
            Line((-8.217823563, 18.23368794), (-10.727884987, 22.581241855))
            ThreePointArc((-10.727884987, 22.581241855), (-12.5, 21.650635095), (-14.191986602, 20.581241855))
            Line((-14.191986602, 20.581241855), (-11.681925179, 16.23368794))
            ThreePointArc((-11.681925179, 16.23368794), (-10, 17.320508076), (-8.217823563, 18.23368794))
        make_face()
        with BuildLine():
            Line((-13.958516724, 14.323400814), (-17.804153934, 17.550273578))
            ThreePointArc((-17.804153934, 17.550273578), (-19.151111078, 16.069690242), (-20.375304373, 14.486095806))
            Line((-20.375304373, 14.486095806), (-16.529667163, 11.259223041))
            ThreePointArc((-16.529667163, 11.259223041), (-15.320888862, 12.855752194), (-13.958516724, 14.323400814))
        make_face()
        with BuildLine():
            ThreePointArc((-22.732979156, 10.402483294), (-23.49231552, 8.550503583), (-24.10105973, 6.643712811))
            Line((-24.10105973, 6.643712811), (-19.383687335, 4.926729675))
            ThreePointArc((-19.383687335, 4.926729675), (-18.793852416, 6.840402867), (-18.015606762, 8.685500159))
            Line((-18.015606762, 8.685500159), (-22.732979156, 10.402483294))
        make_face()
    extrude(amount=-SPLINE_FINS_CUT_18X_DEPTH, mode=Mode.SUBTRACT)


solid = part.part
